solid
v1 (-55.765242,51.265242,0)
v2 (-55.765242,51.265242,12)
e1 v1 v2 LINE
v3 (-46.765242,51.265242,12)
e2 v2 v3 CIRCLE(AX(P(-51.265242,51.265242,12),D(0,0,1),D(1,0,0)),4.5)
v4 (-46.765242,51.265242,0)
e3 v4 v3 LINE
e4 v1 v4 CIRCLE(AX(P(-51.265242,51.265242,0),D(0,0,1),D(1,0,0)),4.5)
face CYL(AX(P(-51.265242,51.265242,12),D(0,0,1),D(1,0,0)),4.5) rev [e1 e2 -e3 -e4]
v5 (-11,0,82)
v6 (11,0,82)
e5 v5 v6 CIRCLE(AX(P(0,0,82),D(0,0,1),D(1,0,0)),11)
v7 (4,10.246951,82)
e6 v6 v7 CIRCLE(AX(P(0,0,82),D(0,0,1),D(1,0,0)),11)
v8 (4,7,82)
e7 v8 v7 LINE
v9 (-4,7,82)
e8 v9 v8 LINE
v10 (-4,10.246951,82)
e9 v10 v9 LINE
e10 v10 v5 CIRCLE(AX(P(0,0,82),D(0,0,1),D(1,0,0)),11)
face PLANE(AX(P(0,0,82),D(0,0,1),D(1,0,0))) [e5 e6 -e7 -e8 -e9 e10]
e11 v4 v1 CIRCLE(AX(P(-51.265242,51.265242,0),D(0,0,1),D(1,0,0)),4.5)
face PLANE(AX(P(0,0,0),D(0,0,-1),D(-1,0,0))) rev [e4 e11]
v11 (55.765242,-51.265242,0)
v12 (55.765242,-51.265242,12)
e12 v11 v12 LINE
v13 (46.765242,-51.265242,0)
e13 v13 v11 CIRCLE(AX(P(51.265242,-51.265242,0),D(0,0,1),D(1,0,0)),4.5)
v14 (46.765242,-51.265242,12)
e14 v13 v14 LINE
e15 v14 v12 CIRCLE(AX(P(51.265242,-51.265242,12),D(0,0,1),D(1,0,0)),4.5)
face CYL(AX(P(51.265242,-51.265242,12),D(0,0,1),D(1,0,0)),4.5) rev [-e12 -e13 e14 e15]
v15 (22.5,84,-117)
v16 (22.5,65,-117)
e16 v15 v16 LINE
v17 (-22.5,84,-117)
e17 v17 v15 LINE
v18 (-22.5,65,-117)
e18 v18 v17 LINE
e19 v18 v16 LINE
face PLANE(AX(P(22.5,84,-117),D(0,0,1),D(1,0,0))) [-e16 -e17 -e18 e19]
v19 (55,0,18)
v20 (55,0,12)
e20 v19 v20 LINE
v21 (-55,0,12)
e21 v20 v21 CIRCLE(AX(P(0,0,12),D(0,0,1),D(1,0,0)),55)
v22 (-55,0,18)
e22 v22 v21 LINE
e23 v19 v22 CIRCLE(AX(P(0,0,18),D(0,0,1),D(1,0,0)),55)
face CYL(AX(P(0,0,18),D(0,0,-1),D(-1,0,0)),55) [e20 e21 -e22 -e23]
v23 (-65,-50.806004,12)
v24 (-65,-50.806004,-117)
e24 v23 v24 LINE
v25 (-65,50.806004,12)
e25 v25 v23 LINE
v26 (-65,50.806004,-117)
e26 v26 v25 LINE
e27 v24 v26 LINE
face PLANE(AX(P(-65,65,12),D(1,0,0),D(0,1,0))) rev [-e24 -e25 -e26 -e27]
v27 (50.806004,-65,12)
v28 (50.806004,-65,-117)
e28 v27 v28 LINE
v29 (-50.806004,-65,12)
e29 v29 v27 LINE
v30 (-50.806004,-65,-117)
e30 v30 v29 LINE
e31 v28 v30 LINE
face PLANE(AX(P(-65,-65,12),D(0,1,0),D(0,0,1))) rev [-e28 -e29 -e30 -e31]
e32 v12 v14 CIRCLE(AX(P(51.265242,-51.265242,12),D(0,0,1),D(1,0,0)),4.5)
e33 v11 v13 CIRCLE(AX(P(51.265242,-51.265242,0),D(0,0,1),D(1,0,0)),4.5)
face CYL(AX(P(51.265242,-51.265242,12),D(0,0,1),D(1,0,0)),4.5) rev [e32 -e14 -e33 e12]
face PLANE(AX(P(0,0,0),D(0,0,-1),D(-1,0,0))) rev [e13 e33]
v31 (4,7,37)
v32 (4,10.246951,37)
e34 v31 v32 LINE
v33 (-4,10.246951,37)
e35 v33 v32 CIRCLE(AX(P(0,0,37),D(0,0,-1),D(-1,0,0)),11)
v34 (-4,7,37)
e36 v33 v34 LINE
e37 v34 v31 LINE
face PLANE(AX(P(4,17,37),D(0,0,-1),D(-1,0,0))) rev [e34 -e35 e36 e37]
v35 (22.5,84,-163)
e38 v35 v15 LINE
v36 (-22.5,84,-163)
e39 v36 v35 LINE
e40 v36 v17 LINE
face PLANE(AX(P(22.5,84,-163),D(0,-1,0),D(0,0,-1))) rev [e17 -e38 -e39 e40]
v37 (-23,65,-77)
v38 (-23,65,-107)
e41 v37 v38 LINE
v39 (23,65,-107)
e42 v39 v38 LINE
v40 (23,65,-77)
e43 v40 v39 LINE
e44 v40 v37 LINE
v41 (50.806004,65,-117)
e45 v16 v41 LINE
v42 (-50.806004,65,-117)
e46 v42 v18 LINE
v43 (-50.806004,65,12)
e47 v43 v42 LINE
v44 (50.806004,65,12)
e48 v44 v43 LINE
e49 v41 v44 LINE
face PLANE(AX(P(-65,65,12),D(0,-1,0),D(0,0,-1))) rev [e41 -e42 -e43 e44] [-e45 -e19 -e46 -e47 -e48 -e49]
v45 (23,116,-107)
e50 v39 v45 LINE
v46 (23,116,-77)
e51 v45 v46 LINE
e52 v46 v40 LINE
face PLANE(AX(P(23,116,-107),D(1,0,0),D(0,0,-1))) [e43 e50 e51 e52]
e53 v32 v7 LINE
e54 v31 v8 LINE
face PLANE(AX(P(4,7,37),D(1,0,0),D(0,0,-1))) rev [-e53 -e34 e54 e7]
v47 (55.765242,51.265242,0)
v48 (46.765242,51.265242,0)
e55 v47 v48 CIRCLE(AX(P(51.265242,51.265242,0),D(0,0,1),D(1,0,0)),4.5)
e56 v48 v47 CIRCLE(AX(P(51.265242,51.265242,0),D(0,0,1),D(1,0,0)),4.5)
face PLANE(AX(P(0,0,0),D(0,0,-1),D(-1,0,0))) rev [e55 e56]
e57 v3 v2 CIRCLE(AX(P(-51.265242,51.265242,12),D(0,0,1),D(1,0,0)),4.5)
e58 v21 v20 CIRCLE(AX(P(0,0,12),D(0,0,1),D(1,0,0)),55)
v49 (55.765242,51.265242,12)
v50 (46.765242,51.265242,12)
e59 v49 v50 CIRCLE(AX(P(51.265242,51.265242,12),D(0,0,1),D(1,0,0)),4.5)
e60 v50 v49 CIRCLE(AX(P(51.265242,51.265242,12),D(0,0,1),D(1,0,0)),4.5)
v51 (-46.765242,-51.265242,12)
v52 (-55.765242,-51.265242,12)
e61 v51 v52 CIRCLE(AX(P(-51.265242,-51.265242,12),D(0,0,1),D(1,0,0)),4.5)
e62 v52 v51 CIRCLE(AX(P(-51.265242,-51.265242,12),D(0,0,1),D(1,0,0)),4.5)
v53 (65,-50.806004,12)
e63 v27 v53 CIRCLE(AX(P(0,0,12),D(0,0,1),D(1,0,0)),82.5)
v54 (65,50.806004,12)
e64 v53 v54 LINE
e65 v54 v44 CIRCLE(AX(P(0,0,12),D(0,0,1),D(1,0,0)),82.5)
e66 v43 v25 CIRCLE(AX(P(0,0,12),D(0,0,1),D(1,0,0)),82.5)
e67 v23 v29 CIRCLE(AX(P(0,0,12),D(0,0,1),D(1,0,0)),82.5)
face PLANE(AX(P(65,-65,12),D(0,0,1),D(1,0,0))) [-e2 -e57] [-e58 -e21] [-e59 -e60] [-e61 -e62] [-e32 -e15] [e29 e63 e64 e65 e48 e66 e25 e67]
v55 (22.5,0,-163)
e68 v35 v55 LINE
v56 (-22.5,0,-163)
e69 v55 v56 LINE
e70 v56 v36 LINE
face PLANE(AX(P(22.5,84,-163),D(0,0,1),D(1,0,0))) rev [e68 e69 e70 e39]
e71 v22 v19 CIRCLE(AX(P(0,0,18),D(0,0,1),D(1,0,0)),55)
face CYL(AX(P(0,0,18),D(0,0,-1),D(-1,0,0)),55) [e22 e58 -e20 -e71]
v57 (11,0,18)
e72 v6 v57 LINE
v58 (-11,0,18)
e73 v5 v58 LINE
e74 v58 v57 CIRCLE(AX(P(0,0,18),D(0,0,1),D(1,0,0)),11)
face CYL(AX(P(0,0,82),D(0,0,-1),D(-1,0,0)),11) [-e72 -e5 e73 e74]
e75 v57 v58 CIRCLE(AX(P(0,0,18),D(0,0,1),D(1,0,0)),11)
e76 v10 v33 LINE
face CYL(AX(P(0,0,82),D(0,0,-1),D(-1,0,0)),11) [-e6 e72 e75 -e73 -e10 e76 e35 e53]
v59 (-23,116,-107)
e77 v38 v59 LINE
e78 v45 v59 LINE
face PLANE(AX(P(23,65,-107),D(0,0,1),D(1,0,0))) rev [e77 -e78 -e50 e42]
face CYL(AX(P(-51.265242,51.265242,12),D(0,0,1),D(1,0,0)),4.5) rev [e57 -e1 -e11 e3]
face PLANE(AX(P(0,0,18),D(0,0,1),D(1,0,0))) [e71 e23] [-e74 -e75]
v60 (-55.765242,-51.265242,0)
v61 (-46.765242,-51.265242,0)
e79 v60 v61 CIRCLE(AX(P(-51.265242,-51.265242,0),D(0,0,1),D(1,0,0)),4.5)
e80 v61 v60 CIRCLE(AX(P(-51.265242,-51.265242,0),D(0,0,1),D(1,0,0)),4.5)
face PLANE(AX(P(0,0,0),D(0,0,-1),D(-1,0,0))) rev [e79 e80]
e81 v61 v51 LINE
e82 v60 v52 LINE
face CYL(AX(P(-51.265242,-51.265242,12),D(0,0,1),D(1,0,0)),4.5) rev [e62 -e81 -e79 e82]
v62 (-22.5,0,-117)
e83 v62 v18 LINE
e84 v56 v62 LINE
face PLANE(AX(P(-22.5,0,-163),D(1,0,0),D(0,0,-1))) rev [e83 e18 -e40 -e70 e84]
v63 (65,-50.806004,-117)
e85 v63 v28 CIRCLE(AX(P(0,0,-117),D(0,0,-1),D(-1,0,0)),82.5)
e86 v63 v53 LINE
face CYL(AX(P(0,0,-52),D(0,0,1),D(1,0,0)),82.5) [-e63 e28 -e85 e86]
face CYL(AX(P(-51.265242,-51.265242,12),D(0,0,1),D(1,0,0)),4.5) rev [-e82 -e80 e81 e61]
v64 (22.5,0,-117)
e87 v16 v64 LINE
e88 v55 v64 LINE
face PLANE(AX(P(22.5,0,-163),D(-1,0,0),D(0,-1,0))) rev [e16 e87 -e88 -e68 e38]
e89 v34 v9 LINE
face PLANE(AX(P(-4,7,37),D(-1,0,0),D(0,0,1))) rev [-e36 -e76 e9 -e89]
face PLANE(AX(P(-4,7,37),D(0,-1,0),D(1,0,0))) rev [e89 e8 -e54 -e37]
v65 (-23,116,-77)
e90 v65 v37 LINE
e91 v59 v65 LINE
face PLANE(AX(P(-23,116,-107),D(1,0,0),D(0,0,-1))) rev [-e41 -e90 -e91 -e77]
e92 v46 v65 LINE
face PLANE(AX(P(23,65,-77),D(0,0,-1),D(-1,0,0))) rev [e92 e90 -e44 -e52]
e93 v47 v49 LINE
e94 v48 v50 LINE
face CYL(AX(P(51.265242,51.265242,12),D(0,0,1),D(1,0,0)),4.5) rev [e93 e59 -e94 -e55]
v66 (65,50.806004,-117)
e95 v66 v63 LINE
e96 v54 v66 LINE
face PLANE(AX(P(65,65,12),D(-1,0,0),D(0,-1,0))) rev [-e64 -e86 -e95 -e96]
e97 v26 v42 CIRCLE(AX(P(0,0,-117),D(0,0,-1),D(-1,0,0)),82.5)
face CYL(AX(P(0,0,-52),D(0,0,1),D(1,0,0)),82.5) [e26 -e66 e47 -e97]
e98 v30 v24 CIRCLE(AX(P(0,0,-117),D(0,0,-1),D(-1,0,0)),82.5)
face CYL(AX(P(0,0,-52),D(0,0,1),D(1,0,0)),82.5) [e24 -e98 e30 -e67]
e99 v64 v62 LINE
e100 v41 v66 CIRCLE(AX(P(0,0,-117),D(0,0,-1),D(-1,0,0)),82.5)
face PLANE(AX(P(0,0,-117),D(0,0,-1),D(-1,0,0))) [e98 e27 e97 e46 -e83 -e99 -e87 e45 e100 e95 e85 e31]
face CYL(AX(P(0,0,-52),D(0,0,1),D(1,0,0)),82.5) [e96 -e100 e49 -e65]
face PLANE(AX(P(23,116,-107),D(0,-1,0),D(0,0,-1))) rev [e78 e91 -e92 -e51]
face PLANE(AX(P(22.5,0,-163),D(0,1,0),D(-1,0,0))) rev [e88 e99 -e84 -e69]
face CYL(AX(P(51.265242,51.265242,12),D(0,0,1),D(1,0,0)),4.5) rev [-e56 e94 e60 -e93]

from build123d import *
from build123d.topology import SkipClean

# Parameters (mm, degrees)
SKETCH1_W           = 130
SKETCH1_H           = 130
BOSS_EXTRUDE1_DEPTH = 12
SKETCH2_R           = 55
BOSS_EXTRUDE2_DEPTH = 6
SKETCH3_R           = 11
BOSS_EXTRUDE3_DEPTH = 64
SKETCH4_OUTSIDE_W   = 172.262
SKETCH4_OUTSIDE_H   = 172.262
SKETCH4_OUTSIDE_R   = 82.5
CUT_EXTRUDE1_DEPTH  = 64
CIRPATTERN1_COUNT   = 4
BOSS_EXTRUDE4_DEPTH = 117
SKETCH8_W           = 45
SKETCH8_H           = 84
BOSS_EXTRUDE5_DEPTH = 46
SKETCH9_W           = 30
SKETCH9_H           = 51
BOSS_EXTRUDE6_DEPTH = 23
SKETCH10_W          = 8
SKETCH10_H          = 10
CUT_EXTRUDE2_DEPTH  = 45


with BuildPart() as part:
    # Sketch1 → Boss-Extrude1 (new body)
    with BuildSketch(Plane.XY):
        Rectangle(SKETCH1_W, SKETCH1_H)
    extrude(amount=BOSS_EXTRUDE1_DEPTH)

    # Sketch2 → Boss-Extrude2 (add)
    with BuildSketch(Plane.XY.offset(12)):
        Circle(SKETCH2_R)
    extrude(amount=BOSS_EXTRUDE2_DEPTH)

    # Sketch3 → Boss-Extrude3 (add)
    with BuildSketch(Plane.XY.offset(18)):
        Circle(SKETCH3_R)
    extrude(amount=BOSS_EXTRUDE3_DEPTH)

    # Sketch4 outside → Cut-Extrude1 (cut)
    with BuildSketch(Plane.XY.offset(12)):
        Rectangle(SKETCH4_OUTSIDE_W, SKETCH4_OUTSIDE_H)
        Circle(SKETCH4_OUTSIDE_R, mode=Mode.SUBTRACT)
    extrude(amount=-CUT_EXTRUDE1_DEPTH, mode=Mode.SUBTRACT)

    # Sketch5 → Ø9.0 (9) Diameter Hole1 (revolve, cut)
    with BuildSketch(Plane(origin=(-51.265241636, 51.265241636, 12), x_dir=(0, -1, 0), z_dir=(1, 0, 0))):
        Polygon((0, 0), (0, 402.703872786), (4.5, 400), (4.5, 0), align=None)
    f_9_0_9_diameter_hole1 = revolve(axis=Axis((-51.265241636, 51.265241636, 18.35), (0, 0, -1)), mode=Mode.SUBTRACT)

    # CirPattern1: Ø9.0 (9) Diameter Hole1 ×4 about axis
    cirpattern1_axis = Axis((0, 0, 0), (0, 0, 1))
    for i in range(1, CIRPATTERN1_COUNT):
        add(f_9_0_9_diameter_hole1.rotate(cirpattern1_axis, i * 360 / CIRPATTERN1_COUNT), mode=Mode.SUBTRACT)

    # Sketch7 → Boss-Extrude4 (add)
    with SkipClean():  # the faces are left unmerged after this step: merging them gives an invalid solid
        with BuildSketch(Plane(origin=(0, 0, 0), x_dir=(-1, 0, 0), z_dir=(0, 0, -1))):
            with BuildLine():
                Line((-65, 50.806003582), (-65, -50.806003582))
                ThreePointArc((-65, -50.806003582), (-58.336309448, -58.336309448), (-50.806003582, -65))
                Line((-50.806003582, -65), (50.806003582, -65))
                ThreePointArc((50.806003582, -65), (58.336309448, -58.336309448), (65, -50.806003582))
                Line((65, -50.806003582), (65, 50.806003582))
                ThreePointArc((65, 50.806003582), (58.336309448, 58.336309448), (50.806003582, 65))
                Line((50.806003582, 65), (-50.806003582, 65))
                ThreePointArc((-50.806003582, 65), (-58.336309448, 58.336309448), (-65, 50.806003582))
            make_face()
        extrude(amount=BOSS_EXTRUDE4_DEPTH)

    # Sketch8 → Boss-Extrude5 (add)
    with SkipClean():  # the faces are left unmerged after this step: merging them gives an invalid solid
        with BuildSketch(Plane(origin=(0, 0, -117), x_dir=(-1, 0, 0), z_dir=(0, 0, -1))):
            with Locations((0, 42)):
                Rectangle(SKETCH8_W, SKETCH8_H)
        extrude(amount=BOSS_EXTRUDE5_DEPTH)

    # Sketch9 → Boss-Extrude6 (add, symmetric)
    with SkipClean():  # the faces are left unmerged after this step: merging them gives an invalid solid
        with BuildSketch(Plane(origin=(0, 0, 0), x_dir=(0, 0, -1), z_dir=(1, 0, 0))):
            with Locations((92, 90.5)):
                Rectangle(SKETCH9_W, SKETCH9_H)
        extrude(amount=BOSS_EXTRUDE6_DEPTH, both=True)

    # Sketch10 → Cut-Extrude2 (cut)
    with SkipClean():  # the faces are left unmerged after this step: merging them gives an invalid solid
        with BuildSketch(Plane.XY.offset(82)):
            with Locations((0, 12)):
                Rectangle(SKETCH10_W, SKETCH10_H)
        extrude(amount=-CUT_EXTRUDE2_DEPTH, mode=Mode.SUBTRACT)


solid = part.part
